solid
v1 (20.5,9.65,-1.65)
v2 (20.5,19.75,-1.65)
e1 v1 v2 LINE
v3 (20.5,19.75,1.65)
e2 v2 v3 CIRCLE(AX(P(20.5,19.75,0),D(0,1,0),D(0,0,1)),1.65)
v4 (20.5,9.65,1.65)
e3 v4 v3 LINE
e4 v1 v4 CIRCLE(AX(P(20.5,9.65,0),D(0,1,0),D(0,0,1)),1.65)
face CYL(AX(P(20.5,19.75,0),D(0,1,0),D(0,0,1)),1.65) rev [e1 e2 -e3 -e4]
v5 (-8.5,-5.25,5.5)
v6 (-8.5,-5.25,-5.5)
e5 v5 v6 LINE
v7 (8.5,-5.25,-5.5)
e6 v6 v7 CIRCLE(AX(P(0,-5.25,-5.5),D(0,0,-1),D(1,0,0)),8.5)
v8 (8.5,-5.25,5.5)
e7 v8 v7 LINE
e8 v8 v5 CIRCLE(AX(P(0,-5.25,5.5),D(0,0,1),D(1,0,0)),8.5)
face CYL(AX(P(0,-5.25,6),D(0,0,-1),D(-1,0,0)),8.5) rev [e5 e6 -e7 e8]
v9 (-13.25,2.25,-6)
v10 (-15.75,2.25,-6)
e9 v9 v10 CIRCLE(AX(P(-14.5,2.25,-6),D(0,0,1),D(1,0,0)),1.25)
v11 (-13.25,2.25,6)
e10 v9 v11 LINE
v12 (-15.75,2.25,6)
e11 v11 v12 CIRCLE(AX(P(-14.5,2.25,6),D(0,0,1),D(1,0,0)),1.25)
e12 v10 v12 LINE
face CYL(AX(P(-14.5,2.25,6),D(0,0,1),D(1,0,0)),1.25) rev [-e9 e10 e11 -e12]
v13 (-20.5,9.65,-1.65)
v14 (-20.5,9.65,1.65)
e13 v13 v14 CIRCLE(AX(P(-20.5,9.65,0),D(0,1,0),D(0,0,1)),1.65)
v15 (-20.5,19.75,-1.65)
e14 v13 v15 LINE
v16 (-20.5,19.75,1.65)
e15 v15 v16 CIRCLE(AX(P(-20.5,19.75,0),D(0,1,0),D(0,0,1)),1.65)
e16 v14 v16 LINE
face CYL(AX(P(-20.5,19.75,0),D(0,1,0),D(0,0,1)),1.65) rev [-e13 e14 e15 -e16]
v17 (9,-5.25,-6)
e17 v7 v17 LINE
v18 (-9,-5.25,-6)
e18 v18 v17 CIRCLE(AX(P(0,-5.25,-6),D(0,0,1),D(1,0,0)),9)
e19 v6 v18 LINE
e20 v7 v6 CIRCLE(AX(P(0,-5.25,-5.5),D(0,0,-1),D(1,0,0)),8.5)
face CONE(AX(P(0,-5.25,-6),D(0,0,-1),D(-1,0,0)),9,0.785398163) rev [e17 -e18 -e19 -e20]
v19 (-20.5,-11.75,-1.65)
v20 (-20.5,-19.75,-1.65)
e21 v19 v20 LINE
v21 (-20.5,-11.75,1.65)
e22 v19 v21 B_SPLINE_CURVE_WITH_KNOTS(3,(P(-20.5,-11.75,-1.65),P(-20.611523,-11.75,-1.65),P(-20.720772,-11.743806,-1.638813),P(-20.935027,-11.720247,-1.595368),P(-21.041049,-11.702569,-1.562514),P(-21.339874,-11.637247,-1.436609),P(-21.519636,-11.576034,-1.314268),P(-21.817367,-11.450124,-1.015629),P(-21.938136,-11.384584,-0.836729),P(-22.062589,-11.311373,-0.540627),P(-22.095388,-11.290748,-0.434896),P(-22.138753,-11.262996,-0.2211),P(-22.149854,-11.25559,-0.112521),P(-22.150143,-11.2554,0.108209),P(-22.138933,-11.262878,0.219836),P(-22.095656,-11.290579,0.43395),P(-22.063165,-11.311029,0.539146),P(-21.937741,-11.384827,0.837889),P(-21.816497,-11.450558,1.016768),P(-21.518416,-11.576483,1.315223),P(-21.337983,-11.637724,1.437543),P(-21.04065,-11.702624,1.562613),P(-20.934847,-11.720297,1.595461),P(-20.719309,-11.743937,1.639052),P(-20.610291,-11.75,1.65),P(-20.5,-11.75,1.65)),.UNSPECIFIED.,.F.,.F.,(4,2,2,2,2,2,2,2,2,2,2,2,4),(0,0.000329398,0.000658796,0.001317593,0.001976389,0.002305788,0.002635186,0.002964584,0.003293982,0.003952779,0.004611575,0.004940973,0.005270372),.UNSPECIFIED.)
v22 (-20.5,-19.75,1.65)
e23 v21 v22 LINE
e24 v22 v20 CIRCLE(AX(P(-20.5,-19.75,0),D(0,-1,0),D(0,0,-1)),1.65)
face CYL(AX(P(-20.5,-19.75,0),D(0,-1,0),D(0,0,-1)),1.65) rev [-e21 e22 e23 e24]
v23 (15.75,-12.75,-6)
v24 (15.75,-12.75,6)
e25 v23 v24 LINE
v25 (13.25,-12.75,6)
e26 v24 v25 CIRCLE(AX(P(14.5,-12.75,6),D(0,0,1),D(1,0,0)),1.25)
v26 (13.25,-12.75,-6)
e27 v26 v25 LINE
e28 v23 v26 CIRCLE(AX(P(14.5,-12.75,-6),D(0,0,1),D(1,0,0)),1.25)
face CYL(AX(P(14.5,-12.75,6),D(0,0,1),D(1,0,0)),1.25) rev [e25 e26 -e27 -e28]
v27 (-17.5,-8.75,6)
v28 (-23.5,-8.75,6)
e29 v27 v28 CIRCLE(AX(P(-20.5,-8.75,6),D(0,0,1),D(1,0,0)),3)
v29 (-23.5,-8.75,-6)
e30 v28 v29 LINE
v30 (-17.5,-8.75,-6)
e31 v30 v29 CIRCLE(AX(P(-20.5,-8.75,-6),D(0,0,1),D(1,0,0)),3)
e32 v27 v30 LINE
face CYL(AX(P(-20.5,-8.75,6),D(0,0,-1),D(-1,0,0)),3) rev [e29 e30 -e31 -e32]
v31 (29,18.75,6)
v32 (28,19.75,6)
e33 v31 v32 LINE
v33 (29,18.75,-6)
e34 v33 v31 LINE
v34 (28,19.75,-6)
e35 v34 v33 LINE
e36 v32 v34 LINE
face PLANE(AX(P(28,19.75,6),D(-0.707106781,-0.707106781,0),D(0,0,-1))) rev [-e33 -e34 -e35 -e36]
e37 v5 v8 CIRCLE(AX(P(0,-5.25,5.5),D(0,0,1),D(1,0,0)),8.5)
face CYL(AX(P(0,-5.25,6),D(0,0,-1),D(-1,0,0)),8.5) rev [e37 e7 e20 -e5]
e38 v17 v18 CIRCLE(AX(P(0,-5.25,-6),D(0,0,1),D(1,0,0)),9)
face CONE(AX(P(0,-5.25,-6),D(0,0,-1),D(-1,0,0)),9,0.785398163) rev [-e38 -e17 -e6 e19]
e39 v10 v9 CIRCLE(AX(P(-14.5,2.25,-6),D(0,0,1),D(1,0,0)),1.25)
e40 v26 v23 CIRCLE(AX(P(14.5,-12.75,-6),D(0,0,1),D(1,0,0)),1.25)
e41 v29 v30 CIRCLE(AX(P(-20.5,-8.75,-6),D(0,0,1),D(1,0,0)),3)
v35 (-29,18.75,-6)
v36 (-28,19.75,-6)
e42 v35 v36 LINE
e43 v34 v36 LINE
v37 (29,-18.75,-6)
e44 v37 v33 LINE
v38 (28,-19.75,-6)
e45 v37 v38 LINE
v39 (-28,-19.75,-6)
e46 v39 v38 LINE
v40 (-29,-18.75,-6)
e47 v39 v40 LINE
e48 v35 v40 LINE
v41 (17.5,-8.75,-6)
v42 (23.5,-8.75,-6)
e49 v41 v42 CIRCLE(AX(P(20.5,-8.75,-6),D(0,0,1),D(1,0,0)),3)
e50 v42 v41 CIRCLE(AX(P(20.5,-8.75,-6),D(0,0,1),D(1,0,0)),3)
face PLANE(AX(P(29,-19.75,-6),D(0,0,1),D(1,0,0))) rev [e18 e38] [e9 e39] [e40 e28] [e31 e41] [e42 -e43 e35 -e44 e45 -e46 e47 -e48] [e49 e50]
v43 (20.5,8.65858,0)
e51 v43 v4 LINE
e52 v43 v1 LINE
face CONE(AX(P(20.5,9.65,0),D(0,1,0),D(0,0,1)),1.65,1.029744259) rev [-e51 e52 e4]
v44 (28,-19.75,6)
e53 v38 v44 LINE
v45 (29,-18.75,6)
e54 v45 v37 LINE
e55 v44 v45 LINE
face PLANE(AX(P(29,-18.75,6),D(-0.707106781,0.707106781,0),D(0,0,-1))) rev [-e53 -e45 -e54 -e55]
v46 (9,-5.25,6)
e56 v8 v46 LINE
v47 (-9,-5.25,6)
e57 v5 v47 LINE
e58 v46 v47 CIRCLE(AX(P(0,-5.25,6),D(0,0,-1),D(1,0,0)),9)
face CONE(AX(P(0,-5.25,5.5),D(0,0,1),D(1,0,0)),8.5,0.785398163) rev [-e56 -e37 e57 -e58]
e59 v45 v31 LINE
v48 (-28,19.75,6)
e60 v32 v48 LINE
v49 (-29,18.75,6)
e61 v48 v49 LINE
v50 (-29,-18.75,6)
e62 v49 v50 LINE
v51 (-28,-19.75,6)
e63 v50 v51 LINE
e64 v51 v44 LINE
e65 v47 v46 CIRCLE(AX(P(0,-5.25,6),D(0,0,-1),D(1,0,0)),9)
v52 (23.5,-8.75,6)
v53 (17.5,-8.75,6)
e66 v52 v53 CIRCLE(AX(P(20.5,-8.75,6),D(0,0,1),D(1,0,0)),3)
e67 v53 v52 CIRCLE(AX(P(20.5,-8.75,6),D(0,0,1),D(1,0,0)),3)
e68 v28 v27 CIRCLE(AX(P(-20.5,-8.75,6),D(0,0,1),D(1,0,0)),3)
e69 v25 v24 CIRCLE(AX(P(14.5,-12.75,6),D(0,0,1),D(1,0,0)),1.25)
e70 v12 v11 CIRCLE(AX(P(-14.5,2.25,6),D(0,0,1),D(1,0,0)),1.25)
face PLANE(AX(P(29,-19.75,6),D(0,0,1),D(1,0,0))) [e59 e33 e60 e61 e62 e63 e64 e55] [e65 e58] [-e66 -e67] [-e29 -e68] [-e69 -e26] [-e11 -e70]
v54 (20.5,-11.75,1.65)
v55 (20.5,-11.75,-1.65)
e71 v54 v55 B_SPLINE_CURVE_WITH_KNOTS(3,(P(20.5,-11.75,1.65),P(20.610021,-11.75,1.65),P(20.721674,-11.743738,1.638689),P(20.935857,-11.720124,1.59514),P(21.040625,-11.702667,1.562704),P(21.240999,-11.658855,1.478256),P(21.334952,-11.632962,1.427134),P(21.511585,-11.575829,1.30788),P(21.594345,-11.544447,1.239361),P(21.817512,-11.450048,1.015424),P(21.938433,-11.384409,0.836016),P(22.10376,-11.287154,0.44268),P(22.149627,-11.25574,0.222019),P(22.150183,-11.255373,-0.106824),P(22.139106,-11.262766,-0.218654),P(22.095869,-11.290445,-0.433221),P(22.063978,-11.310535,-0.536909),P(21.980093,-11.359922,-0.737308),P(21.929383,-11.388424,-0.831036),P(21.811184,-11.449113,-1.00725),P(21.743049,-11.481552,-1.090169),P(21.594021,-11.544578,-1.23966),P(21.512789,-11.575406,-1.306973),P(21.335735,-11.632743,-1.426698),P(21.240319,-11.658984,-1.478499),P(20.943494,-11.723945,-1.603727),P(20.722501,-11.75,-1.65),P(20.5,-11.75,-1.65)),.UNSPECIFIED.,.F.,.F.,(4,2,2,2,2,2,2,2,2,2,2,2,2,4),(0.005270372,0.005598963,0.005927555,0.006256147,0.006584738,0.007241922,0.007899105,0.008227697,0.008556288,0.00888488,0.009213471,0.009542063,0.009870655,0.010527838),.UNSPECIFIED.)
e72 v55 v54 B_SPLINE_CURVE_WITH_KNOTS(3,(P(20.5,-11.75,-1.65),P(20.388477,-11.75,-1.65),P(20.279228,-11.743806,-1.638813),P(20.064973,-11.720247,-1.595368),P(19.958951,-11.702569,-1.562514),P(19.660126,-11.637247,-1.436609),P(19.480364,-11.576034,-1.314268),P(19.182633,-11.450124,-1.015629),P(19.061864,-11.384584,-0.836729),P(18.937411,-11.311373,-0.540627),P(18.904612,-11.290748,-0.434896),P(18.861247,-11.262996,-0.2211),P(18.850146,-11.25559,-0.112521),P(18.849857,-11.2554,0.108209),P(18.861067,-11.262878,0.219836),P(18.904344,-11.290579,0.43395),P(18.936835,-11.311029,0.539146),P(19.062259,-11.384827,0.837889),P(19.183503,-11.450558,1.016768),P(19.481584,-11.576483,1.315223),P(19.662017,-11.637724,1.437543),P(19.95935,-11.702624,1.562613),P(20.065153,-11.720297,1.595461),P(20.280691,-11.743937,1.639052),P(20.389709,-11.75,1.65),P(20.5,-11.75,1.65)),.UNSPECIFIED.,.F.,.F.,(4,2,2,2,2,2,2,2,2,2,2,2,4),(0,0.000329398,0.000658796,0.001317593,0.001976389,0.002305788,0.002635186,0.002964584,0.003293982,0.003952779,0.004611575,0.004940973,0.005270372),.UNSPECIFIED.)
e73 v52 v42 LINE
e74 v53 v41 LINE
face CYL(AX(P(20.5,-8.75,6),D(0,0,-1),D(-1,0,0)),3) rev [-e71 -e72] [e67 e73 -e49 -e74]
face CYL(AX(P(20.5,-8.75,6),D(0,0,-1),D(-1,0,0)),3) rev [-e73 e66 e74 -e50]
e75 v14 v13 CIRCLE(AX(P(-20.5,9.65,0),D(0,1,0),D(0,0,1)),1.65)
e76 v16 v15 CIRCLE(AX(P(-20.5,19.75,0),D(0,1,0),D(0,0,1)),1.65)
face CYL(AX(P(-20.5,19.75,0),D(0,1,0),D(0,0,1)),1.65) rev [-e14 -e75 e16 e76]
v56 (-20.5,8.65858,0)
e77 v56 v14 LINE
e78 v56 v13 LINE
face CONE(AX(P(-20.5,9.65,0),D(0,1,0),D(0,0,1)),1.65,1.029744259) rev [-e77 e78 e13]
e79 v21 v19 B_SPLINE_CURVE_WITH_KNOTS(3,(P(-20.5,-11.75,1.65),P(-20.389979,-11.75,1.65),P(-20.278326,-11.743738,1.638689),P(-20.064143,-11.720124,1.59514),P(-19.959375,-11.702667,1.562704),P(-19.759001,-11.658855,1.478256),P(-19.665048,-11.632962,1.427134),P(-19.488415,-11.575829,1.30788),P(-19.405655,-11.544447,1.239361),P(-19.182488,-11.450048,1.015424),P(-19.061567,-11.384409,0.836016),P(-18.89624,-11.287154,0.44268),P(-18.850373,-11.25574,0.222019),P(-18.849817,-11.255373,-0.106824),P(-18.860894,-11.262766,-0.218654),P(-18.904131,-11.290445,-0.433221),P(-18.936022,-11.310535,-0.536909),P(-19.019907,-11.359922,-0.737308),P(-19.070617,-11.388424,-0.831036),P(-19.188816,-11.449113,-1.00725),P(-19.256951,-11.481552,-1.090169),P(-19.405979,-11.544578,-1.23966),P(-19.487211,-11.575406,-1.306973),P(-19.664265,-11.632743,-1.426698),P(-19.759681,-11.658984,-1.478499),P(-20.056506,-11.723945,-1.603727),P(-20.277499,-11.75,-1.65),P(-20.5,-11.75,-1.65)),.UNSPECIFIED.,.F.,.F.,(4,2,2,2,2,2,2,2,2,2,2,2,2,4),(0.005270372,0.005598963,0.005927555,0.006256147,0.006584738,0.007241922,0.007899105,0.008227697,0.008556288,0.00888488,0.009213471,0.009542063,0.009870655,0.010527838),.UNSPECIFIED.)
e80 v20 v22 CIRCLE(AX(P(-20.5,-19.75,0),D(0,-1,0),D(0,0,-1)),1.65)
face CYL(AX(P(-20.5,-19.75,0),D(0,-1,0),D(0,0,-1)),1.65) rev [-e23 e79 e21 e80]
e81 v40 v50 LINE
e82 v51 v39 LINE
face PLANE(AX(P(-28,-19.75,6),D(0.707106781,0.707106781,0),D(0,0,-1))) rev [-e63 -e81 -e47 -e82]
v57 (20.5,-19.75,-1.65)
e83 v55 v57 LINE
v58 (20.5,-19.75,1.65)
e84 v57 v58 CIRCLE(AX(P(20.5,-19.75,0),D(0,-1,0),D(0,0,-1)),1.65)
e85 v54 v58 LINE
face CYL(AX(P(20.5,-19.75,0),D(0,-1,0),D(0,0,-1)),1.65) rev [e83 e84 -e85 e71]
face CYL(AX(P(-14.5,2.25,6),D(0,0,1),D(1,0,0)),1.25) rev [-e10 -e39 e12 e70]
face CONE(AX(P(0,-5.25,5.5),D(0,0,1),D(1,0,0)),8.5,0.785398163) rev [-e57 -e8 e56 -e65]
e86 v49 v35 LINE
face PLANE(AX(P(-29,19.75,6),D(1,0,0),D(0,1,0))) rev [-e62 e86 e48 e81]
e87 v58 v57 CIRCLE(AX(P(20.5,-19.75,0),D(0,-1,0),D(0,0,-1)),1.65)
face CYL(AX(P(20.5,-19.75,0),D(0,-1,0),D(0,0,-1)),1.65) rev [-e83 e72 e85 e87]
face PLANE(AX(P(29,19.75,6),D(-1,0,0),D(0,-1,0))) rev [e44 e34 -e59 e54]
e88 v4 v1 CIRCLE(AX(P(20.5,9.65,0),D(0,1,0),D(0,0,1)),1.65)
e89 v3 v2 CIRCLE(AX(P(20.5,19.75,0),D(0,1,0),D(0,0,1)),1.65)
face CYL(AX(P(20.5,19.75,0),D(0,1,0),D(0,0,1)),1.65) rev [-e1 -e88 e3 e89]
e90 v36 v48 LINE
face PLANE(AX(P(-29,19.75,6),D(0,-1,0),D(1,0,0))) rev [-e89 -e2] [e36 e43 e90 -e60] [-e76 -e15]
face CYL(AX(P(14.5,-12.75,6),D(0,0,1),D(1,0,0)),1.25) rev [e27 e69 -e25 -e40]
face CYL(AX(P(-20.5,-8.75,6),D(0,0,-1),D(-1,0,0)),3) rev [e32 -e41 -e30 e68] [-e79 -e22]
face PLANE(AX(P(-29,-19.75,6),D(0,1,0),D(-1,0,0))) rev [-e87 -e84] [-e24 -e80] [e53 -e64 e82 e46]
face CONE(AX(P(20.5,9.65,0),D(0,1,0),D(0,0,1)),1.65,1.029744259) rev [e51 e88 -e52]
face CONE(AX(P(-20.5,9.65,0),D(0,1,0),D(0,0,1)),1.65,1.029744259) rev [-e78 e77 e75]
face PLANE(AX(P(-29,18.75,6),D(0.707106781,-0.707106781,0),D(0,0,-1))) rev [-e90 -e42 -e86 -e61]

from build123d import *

# Parameters (mm, degrees)
SKETCH1_W                  = 58
SKETCH1_H                  = 39.5
SKETCH1_R                  = 8.5
SKETCH1_R_2                = 3
BOSS_EXTRUDE1_DEPTH        = 6
M3_TAPPED_HOLE1_D          = 2.5
M4_TAPPED_HOLE1_AT_2_COUNT = 2
M4_TAPPED_HOLE1_AT_2_PITCH = 41
CHAMFER1_SIZE              = 1
CHAMFER2_SIZE              = 0.5


with BuildPart() as part:
    # Sketch1 → Boss-Extrude1 (new, symmetric)
    with BuildSketch(Plane.XY):
        Rectangle(SKETCH1_W, SKETCH1_H)
        with Locations((0, -5.25)):
            Circle(SKETCH1_R, mode=Mode.SUBTRACT)
        with Locations((-20.5, -8.75)):
            Circle(SKETCH1_R_2, mode=Mode.SUBTRACT)
        with Locations((20.5, -8.75)):
            Circle(SKETCH1_R_2, mode=Mode.SUBTRACT)
    extrude(amount=BOSS_EXTRUDE1_DEPTH, both=True)

    # M3 Tapped Hole1 (through all)
    with Locations(Plane.XY.offset(6)):
        with Locations((-14.5, 2.25), (14.5, -12.75)):
            Hole(M3_TAPPED_HOLE1_D / 2)

    # Sketch4 → M4 Tapped Hole1 (revolve, cut)
    with BuildSketch(Plane(origin=(-20.5, -19.75, 0), x_dir=(0, 0, -1), z_dir=(1, 0, 0))):
        Polygon((0, 0), (0, 11.091420021), (1.65, 10.1), (1.65, 0), align=None)
    m4_tapped_hole1 = revolve(axis=Axis((-20.5, -26.1, 0), (0, 1, 0)), mode=Mode.SUBTRACT)

    # M4 Tapped Hole1 at 2: M4 Tapped Hole1 ×2
    with Locations(*[(i * M4_TAPPED_HOLE1_AT_2_PITCH, 0, 0) for i in range(1, M4_TAPPED_HOLE1_AT_2_COUNT)]):
        add(m4_tapped_hole1, mode=Mode.SUBTRACT)

    # Mirror1: M4 Tapped Hole1 across plane
    add(m4_tapped_hole1.mirror(Plane.ZX), mode=Mode.SUBTRACT)

    # Mirror1 copy 1 sketch → Mirror1 copy 1 (revolve, cut)
    with BuildSketch(Plane(origin=(20.5, 19.75, 0), x_dir=(0, 0, -1), z_dir=(1, 0, 0))):
        Polygon((0, 0), (0, -11.091420021), (1.65, -10.1), (1.65, 0), align=None)
    revolve(axis=Axis((20.5, 26.1, 0), (0, 1, 0)), mode=Mode.SUBTRACT)

    # Chamfer1
    chamfer1_edges = [part.edges().sort_by_distance(p)[0] for p in [
        (29, -19.75, 0),
        (-29, -19.75, 0),
        (-29, 19.75, 0),
        (29, 19.75, 0),
    ]]
    chamfer(chamfer1_edges, length=CHAMFER1_SIZE)

    # Chamfer2
    chamfer2_edges = [part.edges().sort_by_distance(p)[0] for p in [
        (-8.5, -5.25, -6),
        (-8.5, -5.25, 6),
    ]]
    chamfer(chamfer2_edges, length=CHAMFER2_SIZE)


solid = part.part
